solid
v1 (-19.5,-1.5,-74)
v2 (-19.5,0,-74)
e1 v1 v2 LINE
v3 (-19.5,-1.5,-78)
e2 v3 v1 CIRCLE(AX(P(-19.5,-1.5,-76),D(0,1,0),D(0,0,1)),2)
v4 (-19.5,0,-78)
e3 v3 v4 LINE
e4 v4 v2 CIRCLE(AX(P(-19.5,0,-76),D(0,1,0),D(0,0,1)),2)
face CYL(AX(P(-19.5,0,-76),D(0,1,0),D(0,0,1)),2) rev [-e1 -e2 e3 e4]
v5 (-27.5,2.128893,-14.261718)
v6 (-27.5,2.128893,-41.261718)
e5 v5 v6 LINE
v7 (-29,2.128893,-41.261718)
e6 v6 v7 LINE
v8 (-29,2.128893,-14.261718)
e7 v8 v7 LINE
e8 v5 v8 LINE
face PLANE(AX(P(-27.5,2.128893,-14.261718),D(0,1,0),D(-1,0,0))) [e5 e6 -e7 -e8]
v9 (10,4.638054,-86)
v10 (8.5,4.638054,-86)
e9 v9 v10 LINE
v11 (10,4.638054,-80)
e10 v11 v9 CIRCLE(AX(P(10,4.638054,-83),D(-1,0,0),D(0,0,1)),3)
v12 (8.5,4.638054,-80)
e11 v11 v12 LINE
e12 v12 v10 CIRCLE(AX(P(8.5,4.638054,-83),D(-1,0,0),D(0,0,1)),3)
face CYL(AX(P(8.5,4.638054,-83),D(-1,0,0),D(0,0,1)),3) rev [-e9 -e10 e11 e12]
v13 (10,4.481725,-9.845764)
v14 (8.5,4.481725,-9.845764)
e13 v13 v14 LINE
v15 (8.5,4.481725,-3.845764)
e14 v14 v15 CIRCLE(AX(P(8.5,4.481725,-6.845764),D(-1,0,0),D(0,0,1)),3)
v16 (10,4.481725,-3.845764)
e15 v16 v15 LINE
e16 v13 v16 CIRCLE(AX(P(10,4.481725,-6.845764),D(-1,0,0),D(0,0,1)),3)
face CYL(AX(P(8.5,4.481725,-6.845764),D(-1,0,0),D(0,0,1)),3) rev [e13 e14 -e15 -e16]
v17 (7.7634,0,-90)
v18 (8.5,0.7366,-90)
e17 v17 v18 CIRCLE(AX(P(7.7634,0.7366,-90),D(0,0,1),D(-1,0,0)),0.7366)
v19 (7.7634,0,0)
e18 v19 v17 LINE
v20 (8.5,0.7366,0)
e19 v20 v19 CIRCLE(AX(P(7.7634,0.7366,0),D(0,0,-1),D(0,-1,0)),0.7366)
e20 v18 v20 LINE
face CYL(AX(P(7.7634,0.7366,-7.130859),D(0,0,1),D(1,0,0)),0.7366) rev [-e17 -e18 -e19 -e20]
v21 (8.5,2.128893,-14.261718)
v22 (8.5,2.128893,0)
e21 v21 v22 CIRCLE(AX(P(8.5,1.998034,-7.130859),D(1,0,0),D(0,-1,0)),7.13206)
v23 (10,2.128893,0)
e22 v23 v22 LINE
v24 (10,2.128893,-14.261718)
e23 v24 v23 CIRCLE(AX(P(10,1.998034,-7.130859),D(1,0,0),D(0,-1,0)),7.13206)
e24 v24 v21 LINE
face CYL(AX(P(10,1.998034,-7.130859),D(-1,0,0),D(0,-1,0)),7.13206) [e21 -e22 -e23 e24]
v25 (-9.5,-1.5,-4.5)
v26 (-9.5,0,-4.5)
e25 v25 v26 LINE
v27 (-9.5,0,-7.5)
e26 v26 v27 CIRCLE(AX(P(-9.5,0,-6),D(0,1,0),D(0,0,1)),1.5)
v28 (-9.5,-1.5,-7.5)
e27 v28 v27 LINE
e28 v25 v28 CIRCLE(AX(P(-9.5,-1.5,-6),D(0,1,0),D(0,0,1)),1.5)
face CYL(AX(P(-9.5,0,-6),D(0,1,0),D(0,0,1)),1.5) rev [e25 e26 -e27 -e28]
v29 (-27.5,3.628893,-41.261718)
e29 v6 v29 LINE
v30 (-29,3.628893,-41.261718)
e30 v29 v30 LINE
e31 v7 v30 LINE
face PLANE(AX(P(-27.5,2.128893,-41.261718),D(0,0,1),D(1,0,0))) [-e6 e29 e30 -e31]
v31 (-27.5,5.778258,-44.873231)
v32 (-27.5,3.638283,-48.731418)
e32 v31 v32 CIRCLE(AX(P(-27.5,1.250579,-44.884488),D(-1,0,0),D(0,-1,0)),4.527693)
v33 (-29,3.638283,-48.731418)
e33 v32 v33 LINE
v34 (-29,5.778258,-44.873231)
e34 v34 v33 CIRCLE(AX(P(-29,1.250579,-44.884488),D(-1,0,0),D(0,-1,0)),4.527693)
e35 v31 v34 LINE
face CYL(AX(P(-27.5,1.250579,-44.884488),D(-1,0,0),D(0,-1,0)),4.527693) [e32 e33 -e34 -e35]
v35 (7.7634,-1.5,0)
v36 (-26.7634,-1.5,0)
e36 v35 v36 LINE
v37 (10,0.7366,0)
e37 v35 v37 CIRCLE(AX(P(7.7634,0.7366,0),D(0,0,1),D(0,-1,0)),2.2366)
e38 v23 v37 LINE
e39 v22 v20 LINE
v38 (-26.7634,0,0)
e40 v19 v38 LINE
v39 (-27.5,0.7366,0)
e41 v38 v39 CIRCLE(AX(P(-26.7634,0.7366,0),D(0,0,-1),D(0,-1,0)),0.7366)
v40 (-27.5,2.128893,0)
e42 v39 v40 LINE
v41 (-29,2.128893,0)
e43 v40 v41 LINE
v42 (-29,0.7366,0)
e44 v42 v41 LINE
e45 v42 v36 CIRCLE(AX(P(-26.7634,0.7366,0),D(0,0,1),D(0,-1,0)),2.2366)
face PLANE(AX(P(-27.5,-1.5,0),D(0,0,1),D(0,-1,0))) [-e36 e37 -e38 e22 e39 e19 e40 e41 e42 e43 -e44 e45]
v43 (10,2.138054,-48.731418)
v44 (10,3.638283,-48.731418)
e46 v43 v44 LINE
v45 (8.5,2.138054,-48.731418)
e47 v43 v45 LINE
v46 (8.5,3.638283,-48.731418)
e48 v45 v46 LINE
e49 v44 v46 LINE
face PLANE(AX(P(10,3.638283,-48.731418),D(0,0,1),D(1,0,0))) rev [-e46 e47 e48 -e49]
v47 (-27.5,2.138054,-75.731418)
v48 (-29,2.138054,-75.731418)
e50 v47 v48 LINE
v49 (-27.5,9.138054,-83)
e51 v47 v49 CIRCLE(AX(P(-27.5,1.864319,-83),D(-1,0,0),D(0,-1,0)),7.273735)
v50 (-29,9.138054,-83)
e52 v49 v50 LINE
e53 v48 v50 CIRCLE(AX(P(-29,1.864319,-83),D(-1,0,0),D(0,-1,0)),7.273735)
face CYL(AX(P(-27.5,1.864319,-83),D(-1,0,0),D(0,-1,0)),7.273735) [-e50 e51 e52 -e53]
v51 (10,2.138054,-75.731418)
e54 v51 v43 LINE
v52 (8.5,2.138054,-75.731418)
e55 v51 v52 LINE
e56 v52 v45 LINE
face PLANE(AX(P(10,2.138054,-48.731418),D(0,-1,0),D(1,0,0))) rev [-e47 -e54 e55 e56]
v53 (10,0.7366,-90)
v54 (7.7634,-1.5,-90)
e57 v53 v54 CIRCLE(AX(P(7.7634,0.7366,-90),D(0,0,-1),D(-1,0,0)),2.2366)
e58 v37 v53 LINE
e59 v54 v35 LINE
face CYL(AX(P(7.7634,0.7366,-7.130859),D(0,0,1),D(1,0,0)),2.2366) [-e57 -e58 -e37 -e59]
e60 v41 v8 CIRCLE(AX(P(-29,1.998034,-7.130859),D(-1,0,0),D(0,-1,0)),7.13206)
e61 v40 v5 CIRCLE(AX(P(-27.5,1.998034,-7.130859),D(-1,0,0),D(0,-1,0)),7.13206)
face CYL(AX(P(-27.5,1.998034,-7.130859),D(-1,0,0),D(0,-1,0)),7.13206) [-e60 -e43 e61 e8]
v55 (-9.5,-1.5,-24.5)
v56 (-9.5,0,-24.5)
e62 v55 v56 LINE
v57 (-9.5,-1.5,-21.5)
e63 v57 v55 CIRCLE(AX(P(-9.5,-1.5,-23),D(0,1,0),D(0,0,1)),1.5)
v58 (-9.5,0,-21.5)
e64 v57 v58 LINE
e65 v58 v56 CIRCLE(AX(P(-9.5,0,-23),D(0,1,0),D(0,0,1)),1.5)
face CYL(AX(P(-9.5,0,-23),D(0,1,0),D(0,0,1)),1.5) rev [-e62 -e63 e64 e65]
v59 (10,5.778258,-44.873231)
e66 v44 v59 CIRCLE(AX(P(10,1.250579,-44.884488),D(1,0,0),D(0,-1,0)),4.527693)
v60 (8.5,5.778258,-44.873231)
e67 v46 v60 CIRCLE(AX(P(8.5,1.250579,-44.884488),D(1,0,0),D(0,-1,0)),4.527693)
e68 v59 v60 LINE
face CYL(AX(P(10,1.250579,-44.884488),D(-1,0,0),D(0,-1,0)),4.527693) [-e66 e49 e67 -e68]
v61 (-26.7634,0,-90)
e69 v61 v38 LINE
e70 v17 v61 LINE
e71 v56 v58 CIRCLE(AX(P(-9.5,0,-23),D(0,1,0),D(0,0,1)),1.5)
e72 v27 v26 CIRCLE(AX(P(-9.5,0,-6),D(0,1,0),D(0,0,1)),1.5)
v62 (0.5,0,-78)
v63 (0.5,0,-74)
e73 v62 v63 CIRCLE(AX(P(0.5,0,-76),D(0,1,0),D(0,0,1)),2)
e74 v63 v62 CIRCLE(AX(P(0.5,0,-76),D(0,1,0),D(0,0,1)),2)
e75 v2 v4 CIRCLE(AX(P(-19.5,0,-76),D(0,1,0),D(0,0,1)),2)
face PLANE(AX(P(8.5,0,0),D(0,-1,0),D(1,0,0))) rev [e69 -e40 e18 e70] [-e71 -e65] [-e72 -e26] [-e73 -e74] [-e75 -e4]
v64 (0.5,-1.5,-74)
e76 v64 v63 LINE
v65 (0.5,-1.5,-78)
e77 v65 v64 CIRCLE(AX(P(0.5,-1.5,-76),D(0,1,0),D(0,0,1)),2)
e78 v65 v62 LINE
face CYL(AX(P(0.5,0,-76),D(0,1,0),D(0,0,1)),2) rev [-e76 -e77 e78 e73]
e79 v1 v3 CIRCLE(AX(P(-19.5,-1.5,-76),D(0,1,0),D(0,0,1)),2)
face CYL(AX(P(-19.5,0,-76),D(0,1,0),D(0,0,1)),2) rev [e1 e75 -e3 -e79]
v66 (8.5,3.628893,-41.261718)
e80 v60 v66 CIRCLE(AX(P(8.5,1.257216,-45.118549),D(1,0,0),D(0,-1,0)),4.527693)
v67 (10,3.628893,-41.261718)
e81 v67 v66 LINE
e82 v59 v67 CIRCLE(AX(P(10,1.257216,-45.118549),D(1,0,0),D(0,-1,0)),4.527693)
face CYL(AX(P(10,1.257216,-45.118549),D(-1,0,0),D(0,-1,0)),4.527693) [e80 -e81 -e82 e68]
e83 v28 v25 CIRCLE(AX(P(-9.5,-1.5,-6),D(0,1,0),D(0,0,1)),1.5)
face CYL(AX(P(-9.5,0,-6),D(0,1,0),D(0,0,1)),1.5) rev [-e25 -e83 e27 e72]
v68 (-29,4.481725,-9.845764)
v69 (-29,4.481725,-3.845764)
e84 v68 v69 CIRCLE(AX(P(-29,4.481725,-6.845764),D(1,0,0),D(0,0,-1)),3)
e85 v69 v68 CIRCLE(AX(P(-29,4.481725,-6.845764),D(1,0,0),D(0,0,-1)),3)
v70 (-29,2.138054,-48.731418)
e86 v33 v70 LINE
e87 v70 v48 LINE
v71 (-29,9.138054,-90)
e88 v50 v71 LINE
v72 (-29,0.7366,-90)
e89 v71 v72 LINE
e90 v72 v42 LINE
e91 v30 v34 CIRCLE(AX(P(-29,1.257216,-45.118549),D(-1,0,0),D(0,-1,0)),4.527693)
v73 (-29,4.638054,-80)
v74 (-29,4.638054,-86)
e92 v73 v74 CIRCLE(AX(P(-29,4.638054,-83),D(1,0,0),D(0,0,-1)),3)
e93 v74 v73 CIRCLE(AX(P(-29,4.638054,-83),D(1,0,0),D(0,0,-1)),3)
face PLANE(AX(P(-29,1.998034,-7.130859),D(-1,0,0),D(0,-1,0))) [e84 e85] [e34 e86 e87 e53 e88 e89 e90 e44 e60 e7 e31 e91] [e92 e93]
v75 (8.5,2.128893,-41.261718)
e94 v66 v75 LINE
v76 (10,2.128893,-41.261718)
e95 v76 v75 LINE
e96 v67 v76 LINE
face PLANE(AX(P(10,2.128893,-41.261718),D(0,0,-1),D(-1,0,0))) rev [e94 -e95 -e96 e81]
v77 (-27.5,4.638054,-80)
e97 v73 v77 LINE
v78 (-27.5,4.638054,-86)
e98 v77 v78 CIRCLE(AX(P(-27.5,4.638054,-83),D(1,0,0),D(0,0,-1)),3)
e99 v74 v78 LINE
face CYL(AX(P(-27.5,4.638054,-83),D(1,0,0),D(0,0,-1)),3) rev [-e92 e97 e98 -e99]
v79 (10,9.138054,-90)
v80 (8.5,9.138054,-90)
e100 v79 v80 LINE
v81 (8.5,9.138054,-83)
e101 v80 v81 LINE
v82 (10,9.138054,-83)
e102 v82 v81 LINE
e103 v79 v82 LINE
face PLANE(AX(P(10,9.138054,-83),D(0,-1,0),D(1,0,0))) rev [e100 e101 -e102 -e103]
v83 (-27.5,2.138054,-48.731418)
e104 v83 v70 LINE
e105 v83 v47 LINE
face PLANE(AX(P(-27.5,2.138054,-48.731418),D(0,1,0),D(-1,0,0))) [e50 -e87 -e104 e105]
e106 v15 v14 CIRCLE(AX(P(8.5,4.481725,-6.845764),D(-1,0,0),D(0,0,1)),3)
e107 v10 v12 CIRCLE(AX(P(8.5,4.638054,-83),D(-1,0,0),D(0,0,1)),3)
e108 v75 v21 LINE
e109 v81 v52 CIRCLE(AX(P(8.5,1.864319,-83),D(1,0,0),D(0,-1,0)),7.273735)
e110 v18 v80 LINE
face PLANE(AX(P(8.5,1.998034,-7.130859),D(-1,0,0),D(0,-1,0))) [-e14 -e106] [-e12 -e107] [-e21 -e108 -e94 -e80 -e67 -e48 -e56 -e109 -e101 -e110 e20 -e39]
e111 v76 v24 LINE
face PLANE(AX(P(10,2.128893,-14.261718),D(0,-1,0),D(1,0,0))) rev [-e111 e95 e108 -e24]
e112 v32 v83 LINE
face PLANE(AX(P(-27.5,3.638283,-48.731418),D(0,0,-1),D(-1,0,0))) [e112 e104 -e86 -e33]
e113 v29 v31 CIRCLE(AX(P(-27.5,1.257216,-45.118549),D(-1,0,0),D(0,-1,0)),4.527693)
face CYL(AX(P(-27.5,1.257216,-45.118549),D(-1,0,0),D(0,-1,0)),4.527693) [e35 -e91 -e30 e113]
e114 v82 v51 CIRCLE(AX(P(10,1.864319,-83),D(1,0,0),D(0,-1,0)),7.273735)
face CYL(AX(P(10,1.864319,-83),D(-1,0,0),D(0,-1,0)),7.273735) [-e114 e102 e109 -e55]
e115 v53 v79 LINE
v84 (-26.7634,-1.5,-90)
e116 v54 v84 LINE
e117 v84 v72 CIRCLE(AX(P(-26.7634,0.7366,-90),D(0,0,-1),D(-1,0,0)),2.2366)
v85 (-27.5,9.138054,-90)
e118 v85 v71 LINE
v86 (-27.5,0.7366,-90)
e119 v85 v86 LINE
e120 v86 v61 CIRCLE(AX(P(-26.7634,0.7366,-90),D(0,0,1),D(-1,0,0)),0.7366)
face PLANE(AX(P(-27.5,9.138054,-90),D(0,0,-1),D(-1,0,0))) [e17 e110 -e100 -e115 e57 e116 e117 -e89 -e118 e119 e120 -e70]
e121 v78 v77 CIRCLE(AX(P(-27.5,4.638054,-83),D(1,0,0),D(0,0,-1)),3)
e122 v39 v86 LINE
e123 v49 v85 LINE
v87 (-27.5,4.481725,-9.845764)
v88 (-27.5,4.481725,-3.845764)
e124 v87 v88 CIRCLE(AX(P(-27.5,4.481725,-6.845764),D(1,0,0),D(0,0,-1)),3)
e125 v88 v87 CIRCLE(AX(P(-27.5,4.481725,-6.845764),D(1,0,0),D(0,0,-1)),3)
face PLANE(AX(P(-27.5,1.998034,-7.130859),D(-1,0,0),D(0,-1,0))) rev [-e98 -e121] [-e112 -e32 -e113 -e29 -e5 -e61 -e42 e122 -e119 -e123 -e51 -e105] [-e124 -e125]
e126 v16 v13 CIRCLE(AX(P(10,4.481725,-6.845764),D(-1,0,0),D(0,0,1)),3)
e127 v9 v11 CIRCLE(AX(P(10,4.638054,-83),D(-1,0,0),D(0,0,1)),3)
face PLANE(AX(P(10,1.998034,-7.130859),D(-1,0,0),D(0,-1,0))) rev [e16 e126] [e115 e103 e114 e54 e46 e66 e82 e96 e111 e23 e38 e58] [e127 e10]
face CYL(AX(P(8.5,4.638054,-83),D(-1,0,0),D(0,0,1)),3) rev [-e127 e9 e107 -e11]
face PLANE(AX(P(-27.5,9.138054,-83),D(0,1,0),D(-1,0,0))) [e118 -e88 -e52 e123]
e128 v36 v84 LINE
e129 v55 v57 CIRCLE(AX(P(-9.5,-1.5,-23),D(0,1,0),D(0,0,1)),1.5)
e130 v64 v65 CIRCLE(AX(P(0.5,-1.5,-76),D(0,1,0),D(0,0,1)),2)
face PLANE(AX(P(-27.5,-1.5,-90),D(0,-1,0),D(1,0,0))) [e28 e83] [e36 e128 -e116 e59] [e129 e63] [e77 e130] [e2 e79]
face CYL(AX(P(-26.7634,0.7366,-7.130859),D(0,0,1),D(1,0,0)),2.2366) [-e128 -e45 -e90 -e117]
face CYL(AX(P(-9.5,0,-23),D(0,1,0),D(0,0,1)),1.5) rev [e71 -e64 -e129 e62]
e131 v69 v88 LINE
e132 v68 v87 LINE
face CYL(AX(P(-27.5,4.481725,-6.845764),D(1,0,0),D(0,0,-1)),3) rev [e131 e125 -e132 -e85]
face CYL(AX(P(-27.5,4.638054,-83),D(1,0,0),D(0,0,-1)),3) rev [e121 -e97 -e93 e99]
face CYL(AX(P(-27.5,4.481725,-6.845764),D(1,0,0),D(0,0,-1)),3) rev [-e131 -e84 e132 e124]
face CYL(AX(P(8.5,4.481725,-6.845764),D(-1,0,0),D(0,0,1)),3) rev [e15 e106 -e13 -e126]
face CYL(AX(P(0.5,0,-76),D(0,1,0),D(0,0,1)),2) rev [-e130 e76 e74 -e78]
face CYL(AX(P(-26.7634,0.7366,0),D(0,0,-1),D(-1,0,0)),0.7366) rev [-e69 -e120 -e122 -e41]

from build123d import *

# Parameters (mm, degrees)
BOSS_EXTRUDE1_DEPTH          = 1.5
SKETCH2_W                    = 90
SKETCH2_H                    = 1.5
BOSS_EXTRUDE2_DEPTH          = 36
BOSS_EXTRUDE3_DEPTH          = 1.5
F_6_0_6_DIAMETER_HOLE1_D     = 6
F_6_0_6_DIAMETER_HOLE1_DEPTH = 1.5
F_6_0_6_DIAMETER_HOLE2_D     = 6
F_4_0_4_DIAMETER_HOLE1_D     = 4
F_3_0_3_DIAMETER_HOLE1_D     = 3
FILLET1_R                    = 0.7366
FILLET2_R                    = 2.2366


with BuildPart() as part:
    # Sketch1 → Boss-Extrude1 (new body)
    with BuildSketch(Plane(origin=(-29, 0, 0), x_dir=(0, -1, 0), z_dir=(-1, 0, 0))):
        with BuildLine():
            Line((-9.138054181, -90), (1.5, -90))
            Line((1.5, -90), (1.5, 0))
            Line((1.5, 0), (-2.128893479, 0))
            ThreePointArc((-2.128893479, 0), (-9.130094082, -7.130859089), (-2.128893479, -14.261718178))
            Line((-2.128893479, -14.261718178), (-2.128893479, -41.261718178))
            Line((-2.128893479, -41.261718178), (-3.628893479, -41.261718178))
            ThreePointArc((-3.628893479, -41.261718178), (-5.147993713, -42.802982792), (-5.778257675, -44.873231442))
            ThreePointArc((-5.778257675, -44.873231442), (-5.210002115, -47.08061414), (-3.638283373, -48.73141787))
            Line((-3.638283373, -48.73141787), (-2.138054181, -48.73141787))
            Line((-2.138054181, -48.73141787), (-2.138054181, -75.73141787))
            ThreePointArc((-2.138054181, -75.73141787), (-7.103512649, -77.954400774), (-9.138054181, -83))
            Line((-9.138054181, -83), (-9.138054181, -90))
        make_face()
    extrude(amount=-BOSS_EXTRUDE1_DEPTH)

    # Sketch2 → Boss-Extrude2 (add)
    with BuildSketch(Plane(origin=(-27.5, 0, 0), x_dir=(0, 0, -1), z_dir=(1, 0, 0))):
        with Locations((45, -0.75)):
            Rectangle(SKETCH2_W, SKETCH2_H)
    extrude(amount=BOSS_EXTRUDE2_DEPTH)

    # Sketch3 → Boss-Extrude3 (add)
    with BuildSketch(Plane(origin=(8.5, 0, 0), x_dir=(0, 0, -1), z_dir=(1, 0, 0))):
        with BuildLine():
            Line((0, -1.5), (0, 2.128893479))
            ThreePointArc((0, 2.128893479), (7.130859089, 9.130094082), (14.261718178, 2.128893479))
            Line((14.261718178, 2.128893479), (41.261718178, 2.128893479))
            Line((41.261718178, 2.128893479), (41.261718178, 3.628893479))
            ThreePointArc((41.261718178, 3.628893479), (42.802982792, 5.147993713), (44.873231442, 5.778257675))
            ThreePointArc((44.873231442, 5.778257675), (47.08061414, 5.210002115), (48.73141787, 3.638283373))
            Line((48.73141787, 3.638283373), (48.73141787, 2.138054181))
            Line((48.73141787, 2.138054181), (75.73141787, 2.138054181))
            ThreePointArc((75.73141787, 2.138054181), (77.954400774, 7.103512649), (83, 9.138054181))
            Line((83, 9.138054181), (90, 9.138054181))
            Line((90, 9.138054181), (90, -1.5))
            Line((90, -1.5), (0, -1.5))
        make_face()
    extrude(amount=BOSS_EXTRUDE3_DEPTH)

    # Ø6.0 (6) Diameter Hole1
    with Locations(Plane.ZY.offset(-8.5)):
        with Locations((-6.845764439, 4.481725402), (-83, 4.638054181)):
            Hole(F_6_0_6_DIAMETER_HOLE1_D / 2, depth=F_6_0_6_DIAMETER_HOLE1_DEPTH)

    # Ø6.0 (6) Diameter Hole2 (through all)
    with Locations(Plane(origin=(-27.5, 0, 0), x_dir=(0, 0, -1), z_dir=(1, 0, 0))):
        with Locations((83, 4.638054181), (6.845764439, 4.481725402)):
            Hole(F_6_0_6_DIAMETER_HOLE2_D / 2)

    # Ø4.0 (4) Diameter Hole1 (through all)
    with Locations(Plane(origin=(0, 0, 0), x_dir=(1, 0, 0), z_dir=(0, 1, 0))):
        with Locations((-19.5, 76), (0.5, 76)):
            Hole(F_4_0_4_DIAMETER_HOLE1_D / 2)

    # Ø3.0 (3) Diameter Hole1 (through all)
    with Locations(Plane(origin=(0, 0, 0), x_dir=(1, 0, 0), z_dir=(0, 1, 0))):
        with Locations((-9.5, 6), (-9.5, 23)):
            Hole(F_3_0_3_DIAMETER_HOLE1_D / 2)

    # Fillet1
    fillet1_edges = [part.edges().sort_by_distance(p)[0] for p in [
        (-27.5, 0, -45),
        (8.5, 0, -45),
    ]]
    fillet(fillet1_edges, radius=FILLET1_R)

    # Fillet2
    fillet2_edges = [part.edges().sort_by_distance(p)[0] for p in [
        (-29, -1.5, -45),
        (10, -1.5, -45),
    ]]
    fillet(fillet2_edges, radius=FILLET2_R)


solid = part.part
